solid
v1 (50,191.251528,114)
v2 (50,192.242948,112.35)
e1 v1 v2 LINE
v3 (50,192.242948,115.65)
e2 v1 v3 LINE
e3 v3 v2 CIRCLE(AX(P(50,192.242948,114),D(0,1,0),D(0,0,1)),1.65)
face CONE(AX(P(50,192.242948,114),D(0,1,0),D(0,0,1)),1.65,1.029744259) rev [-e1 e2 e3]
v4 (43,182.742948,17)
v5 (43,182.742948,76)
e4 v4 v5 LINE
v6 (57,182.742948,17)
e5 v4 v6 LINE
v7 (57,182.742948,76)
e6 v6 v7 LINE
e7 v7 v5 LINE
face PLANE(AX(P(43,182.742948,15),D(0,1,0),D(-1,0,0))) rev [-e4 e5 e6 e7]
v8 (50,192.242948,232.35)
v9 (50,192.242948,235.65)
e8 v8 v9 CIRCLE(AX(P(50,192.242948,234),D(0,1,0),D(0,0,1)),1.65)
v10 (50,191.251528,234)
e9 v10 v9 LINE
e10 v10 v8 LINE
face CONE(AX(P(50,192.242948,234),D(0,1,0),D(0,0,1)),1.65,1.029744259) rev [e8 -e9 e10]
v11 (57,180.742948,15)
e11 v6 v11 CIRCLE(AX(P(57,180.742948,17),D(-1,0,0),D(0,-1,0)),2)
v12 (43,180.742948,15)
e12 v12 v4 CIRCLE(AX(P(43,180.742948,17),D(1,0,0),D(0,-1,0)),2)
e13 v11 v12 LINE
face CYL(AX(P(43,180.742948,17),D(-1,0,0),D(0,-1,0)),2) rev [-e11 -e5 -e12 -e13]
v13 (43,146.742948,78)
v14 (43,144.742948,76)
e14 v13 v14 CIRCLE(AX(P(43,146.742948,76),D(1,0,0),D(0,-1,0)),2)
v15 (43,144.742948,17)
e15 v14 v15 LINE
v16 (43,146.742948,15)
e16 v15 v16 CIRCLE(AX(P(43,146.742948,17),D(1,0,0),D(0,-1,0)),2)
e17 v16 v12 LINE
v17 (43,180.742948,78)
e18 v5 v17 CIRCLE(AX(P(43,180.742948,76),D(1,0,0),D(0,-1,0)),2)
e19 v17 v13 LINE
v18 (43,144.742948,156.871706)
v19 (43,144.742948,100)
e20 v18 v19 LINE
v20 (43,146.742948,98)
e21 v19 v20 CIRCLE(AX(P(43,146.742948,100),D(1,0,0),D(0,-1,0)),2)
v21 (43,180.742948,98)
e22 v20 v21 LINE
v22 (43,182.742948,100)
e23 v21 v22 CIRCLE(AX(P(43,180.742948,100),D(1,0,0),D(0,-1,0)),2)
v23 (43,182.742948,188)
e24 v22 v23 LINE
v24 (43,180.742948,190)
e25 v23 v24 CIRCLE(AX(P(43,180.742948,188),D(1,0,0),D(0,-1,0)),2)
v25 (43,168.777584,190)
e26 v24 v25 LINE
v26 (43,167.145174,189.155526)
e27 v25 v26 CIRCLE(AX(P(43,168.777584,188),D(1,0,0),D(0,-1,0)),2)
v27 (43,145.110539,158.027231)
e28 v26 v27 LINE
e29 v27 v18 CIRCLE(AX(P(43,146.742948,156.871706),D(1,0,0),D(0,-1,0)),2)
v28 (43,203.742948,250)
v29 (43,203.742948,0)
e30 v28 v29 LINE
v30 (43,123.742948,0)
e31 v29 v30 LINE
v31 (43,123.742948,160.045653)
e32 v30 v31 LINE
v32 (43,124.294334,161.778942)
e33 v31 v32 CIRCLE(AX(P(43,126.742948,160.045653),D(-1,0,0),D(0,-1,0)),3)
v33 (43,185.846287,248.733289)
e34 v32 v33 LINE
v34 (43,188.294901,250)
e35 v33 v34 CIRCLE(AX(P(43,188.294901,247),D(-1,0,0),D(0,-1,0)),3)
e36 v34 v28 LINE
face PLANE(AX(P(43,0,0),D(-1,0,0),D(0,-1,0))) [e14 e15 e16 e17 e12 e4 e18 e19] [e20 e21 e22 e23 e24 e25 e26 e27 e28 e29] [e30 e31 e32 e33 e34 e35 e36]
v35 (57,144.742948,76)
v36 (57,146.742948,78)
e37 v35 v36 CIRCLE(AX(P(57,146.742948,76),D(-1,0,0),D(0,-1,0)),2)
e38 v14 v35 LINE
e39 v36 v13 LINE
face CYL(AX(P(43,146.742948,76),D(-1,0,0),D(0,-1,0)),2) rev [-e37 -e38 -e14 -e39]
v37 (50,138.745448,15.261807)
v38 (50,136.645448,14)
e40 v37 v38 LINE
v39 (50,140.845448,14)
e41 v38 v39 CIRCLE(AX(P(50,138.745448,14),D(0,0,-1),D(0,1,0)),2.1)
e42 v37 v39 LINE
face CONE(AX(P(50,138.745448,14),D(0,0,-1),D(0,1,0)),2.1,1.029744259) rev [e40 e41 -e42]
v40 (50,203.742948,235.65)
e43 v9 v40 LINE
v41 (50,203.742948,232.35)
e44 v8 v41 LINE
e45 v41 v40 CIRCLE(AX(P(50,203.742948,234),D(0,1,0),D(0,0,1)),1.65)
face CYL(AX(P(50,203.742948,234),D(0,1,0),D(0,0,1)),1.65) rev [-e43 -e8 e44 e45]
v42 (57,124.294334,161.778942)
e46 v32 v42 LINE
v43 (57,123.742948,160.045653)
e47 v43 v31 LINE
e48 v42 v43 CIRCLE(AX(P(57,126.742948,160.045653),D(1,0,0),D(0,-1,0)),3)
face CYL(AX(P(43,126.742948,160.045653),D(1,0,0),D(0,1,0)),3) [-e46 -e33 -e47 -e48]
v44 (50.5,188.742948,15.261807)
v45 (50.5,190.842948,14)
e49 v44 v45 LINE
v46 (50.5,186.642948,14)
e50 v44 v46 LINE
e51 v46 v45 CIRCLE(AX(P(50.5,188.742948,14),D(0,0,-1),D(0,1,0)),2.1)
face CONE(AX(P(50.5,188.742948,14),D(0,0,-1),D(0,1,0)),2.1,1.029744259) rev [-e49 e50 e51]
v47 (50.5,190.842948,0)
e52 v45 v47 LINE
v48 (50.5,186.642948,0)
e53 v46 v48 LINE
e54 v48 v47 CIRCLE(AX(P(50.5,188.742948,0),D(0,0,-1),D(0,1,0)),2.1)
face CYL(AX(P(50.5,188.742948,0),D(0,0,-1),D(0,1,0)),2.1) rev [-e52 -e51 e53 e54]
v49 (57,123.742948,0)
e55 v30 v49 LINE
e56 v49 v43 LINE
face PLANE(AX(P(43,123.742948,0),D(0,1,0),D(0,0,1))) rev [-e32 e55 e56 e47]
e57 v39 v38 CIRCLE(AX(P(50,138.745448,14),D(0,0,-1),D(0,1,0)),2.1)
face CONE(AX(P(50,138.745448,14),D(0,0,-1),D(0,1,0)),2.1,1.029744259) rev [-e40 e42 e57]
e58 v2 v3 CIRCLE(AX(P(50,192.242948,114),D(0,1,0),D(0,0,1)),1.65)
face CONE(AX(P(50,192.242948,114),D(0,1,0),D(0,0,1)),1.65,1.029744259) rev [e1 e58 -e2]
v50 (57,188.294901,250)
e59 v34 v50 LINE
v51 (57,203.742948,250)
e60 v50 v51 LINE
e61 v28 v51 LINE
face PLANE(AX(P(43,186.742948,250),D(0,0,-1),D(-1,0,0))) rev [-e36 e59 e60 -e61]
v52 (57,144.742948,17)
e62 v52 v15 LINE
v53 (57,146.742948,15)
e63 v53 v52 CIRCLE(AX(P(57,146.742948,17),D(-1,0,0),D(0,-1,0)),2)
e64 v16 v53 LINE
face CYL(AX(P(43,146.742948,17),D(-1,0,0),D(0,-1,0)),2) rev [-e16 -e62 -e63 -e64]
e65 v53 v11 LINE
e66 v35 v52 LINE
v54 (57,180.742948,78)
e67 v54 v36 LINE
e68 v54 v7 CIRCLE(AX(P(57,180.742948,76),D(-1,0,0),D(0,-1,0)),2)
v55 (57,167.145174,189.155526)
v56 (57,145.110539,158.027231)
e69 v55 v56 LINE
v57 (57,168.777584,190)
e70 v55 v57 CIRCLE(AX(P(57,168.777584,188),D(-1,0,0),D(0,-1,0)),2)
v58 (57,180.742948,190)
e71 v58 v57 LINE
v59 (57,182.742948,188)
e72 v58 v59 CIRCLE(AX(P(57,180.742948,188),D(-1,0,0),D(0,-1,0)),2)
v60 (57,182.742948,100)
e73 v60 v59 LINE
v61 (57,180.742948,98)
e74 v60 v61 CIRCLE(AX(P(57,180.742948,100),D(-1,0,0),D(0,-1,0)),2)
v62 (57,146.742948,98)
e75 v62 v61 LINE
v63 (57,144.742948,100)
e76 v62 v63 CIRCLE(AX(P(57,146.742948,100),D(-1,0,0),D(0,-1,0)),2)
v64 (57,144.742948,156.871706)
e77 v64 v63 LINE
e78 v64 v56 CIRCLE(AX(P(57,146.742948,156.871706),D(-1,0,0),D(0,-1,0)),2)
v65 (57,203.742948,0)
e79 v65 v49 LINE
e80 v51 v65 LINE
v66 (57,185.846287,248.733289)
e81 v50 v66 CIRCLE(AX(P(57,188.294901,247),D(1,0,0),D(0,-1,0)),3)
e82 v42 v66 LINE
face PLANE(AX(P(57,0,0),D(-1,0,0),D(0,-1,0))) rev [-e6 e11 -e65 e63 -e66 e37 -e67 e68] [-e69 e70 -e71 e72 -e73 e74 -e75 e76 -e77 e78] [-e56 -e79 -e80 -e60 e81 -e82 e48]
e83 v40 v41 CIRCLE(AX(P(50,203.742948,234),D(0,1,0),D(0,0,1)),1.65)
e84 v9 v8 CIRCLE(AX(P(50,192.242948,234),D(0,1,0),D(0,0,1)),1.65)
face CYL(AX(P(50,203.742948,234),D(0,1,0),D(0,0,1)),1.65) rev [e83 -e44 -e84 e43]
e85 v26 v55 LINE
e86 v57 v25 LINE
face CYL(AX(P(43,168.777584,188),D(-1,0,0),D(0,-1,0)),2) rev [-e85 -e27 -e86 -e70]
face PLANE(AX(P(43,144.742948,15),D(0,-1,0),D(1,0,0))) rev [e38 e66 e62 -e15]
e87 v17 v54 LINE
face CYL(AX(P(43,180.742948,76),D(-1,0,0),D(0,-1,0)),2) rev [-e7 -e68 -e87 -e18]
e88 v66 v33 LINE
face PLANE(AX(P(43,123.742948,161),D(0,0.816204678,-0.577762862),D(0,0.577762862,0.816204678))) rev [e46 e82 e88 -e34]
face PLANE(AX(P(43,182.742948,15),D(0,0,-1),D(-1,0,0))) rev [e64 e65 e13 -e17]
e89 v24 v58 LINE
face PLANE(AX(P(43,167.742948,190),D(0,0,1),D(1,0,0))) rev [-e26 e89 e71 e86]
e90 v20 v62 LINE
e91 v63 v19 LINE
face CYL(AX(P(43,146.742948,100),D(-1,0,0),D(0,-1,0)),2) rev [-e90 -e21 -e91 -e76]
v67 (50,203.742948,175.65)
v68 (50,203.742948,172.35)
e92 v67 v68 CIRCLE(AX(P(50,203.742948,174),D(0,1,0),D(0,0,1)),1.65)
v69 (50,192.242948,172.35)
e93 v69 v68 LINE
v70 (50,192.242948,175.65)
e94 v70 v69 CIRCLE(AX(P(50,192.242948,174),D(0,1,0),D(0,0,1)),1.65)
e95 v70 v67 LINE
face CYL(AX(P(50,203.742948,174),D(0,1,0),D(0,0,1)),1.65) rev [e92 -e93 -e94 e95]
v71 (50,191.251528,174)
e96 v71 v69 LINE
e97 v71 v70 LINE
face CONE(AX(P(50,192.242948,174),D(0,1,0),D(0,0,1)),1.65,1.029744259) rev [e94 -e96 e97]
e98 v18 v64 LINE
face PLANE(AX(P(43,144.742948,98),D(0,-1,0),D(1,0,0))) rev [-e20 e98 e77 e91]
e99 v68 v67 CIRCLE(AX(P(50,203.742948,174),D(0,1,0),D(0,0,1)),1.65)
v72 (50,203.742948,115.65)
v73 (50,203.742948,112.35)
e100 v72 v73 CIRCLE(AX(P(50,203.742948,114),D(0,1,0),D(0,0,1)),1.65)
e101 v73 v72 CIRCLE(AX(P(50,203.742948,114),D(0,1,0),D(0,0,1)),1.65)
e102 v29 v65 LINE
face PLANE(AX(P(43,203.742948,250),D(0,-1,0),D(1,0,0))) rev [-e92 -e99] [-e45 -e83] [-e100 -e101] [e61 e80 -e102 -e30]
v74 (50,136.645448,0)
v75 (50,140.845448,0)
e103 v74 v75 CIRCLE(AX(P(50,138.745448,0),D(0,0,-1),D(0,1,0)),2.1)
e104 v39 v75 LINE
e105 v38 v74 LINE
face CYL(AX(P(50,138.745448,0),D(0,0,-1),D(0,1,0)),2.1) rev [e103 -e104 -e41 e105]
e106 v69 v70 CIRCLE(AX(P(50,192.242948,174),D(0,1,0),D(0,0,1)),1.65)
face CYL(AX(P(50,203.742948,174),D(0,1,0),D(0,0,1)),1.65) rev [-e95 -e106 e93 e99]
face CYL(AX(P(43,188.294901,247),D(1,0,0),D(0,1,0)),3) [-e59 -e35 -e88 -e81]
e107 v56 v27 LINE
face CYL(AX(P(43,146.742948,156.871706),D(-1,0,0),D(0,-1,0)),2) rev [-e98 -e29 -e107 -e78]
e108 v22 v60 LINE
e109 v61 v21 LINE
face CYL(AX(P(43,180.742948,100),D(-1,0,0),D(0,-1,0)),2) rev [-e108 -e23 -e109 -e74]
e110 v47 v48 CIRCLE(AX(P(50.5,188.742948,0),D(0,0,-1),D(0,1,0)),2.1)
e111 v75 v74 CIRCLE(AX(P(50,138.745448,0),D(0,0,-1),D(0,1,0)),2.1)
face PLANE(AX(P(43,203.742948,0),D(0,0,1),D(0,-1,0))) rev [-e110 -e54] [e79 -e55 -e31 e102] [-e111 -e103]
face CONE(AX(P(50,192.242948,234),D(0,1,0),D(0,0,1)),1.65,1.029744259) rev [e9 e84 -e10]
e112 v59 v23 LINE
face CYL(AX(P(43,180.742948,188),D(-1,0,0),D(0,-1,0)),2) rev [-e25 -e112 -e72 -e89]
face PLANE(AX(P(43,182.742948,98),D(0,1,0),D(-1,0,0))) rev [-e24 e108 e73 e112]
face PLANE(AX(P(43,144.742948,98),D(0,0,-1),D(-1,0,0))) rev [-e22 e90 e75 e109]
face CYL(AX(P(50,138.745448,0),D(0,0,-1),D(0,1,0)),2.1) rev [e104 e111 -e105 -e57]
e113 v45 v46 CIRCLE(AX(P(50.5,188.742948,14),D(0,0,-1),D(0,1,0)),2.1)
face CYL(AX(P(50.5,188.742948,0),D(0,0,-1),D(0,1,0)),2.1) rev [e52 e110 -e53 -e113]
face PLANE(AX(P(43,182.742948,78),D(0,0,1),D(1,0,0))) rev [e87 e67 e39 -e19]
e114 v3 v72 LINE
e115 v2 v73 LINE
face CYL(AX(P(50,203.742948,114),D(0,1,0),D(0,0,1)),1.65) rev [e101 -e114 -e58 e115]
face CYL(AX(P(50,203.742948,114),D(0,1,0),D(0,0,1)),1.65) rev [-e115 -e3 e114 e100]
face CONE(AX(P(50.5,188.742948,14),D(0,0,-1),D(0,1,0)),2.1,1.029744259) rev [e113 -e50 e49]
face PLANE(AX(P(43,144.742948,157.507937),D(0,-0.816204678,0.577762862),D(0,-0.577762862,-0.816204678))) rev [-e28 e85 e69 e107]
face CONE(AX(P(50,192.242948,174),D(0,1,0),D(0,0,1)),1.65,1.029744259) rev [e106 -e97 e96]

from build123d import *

# Parameters (mm, degrees)
BOSS_EXTRUDE1_DEPTH   = 7
SKETCH4_W             = 63
SKETCH4_H             = 38
CUT_EXTRUDE1_DEPTH    = 323.811382974
FILLET1_R             = 2
CUT_EXTRUDE2_DEPTH    = 323.811382974
FILLET2_R             = 2
M5_TAPPED_HOLE1_D     = 4.2
M5_TAPPED_HOLE1_DEPTH = 14
M5_TAPPED_HOLE1_TIP   = 1.2618073
M4_TAPPED_HOLE1_D     = 3.3
M4_TAPPED_HOLE1_DEPTH = 11.5
M4_TAPPED_HOLE1_TIP   = 0.991420021
FILLET3_R             = 3


with BuildPart() as part:
    # Sketch3 → Boss-Extrude1 (new, symmetric)
    with BuildSketch(Plane(origin=(50, 414.547428979, -101), x_dir=(0, 0, -1), z_dir=(-1, 0, 0))):
        Polygon((-101, 210.80448069), (-101, 290.80448069), (-262, 290.80448069), (-351, 227.80448069), (-351, 210.80448069), align=None)
    extrude(amount=BOSS_EXTRUDE1_DEPTH, both=True)

    # Sketch4 → Cut-Extrude1 (cut, through all)
    with BuildSketch(Plane(origin=(57, 0, 0), x_dir=(0, 0, -1), z_dir=(1, 0, 0))):
        with Locations((-46.5, 163.74294829)):
            Rectangle(SKETCH4_W, SKETCH4_H)
    extrude(amount=-CUT_EXTRUDE1_DEPTH, mode=Mode.SUBTRACT)

    # Fillet1
    fillet1_edges = [part.edges().sort_by_distance(p)[0] for p in [
        (50, 182.74294829, 15),
        (50, 144.74294829, 15),
        (50, 144.74294829, 78),
        (50, 182.74294829, 78),
    ]]
    fillet(fillet1_edges, radius=FILLET1_R)

    # Sketch5 → Cut-Extrude2 (cut, through all)
    with BuildSketch(Plane(origin=(57, 0, 0), x_dir=(0, 0, -1), z_dir=(1, 0, 0))):
        Polygon((-98, 144.74294829), (-157.507936508, 144.74294829), (-190, 167.74294829), (-190, 182.74294829), (-98, 182.74294829), align=None)
    extrude(amount=-CUT_EXTRUDE2_DEPTH, mode=Mode.SUBTRACT)

    # Fillet2
    fillet2_edges = [part.edges().sort_by_distance(p)[0] for p in [
        (50, 182.74294829, 98),
        (50, 144.74294829, 98),
        (50, 144.74294829, 157.507936508),
        (50, 167.74294829, 190),
        (50, 182.74294829, 190),
    ]]
    fillet(fillet2_edges, radius=FILLET2_R)

    # M5 Tapped Hole1
    with Locations(Plane(origin=(0, 0, 0), x_dir=(-1, 0, 0), z_dir=(0, 0, -1))):
        with Locations((-50.5, 188.74294829), (-50, 138.745448352)):
            Hole(M5_TAPPED_HOLE1_D / 2, depth=M5_TAPPED_HOLE1_DEPTH)
            with Locations((0, 0, -(M5_TAPPED_HOLE1_DEPTH + M5_TAPPED_HOLE1_TIP / 2))):  # 118° drill point
                Cone(0, M5_TAPPED_HOLE1_D / 2, M5_TAPPED_HOLE1_TIP, mode=Mode.SUBTRACT)

    # M4 Tapped Hole1
    with Locations(Plane(origin=(0, 203.74294829, 0), x_dir=(1, 0, 0), z_dir=(0, 1, 0))):
        with Locations((50, -114), (50, -174), (50, -234)):
            Hole(M4_TAPPED_HOLE1_D / 2, depth=M4_TAPPED_HOLE1_DEPTH)
            with Locations((0, 0, -(M4_TAPPED_HOLE1_DEPTH + M4_TAPPED_HOLE1_TIP / 2))):  # 118° drill point
                Cone(0, M4_TAPPED_HOLE1_D / 2, M4_TAPPED_HOLE1_TIP, mode=Mode.SUBTRACT)

    # Fillet3
    fillet3_edges = [part.edges().sort_by_distance(p)[0] for p in [
        (50, 186.74294829, 250),
        (50, 123.74294829, 161),
    ]]
    fillet(fillet3_edges, radius=FILLET3_R)


solid = part.part
